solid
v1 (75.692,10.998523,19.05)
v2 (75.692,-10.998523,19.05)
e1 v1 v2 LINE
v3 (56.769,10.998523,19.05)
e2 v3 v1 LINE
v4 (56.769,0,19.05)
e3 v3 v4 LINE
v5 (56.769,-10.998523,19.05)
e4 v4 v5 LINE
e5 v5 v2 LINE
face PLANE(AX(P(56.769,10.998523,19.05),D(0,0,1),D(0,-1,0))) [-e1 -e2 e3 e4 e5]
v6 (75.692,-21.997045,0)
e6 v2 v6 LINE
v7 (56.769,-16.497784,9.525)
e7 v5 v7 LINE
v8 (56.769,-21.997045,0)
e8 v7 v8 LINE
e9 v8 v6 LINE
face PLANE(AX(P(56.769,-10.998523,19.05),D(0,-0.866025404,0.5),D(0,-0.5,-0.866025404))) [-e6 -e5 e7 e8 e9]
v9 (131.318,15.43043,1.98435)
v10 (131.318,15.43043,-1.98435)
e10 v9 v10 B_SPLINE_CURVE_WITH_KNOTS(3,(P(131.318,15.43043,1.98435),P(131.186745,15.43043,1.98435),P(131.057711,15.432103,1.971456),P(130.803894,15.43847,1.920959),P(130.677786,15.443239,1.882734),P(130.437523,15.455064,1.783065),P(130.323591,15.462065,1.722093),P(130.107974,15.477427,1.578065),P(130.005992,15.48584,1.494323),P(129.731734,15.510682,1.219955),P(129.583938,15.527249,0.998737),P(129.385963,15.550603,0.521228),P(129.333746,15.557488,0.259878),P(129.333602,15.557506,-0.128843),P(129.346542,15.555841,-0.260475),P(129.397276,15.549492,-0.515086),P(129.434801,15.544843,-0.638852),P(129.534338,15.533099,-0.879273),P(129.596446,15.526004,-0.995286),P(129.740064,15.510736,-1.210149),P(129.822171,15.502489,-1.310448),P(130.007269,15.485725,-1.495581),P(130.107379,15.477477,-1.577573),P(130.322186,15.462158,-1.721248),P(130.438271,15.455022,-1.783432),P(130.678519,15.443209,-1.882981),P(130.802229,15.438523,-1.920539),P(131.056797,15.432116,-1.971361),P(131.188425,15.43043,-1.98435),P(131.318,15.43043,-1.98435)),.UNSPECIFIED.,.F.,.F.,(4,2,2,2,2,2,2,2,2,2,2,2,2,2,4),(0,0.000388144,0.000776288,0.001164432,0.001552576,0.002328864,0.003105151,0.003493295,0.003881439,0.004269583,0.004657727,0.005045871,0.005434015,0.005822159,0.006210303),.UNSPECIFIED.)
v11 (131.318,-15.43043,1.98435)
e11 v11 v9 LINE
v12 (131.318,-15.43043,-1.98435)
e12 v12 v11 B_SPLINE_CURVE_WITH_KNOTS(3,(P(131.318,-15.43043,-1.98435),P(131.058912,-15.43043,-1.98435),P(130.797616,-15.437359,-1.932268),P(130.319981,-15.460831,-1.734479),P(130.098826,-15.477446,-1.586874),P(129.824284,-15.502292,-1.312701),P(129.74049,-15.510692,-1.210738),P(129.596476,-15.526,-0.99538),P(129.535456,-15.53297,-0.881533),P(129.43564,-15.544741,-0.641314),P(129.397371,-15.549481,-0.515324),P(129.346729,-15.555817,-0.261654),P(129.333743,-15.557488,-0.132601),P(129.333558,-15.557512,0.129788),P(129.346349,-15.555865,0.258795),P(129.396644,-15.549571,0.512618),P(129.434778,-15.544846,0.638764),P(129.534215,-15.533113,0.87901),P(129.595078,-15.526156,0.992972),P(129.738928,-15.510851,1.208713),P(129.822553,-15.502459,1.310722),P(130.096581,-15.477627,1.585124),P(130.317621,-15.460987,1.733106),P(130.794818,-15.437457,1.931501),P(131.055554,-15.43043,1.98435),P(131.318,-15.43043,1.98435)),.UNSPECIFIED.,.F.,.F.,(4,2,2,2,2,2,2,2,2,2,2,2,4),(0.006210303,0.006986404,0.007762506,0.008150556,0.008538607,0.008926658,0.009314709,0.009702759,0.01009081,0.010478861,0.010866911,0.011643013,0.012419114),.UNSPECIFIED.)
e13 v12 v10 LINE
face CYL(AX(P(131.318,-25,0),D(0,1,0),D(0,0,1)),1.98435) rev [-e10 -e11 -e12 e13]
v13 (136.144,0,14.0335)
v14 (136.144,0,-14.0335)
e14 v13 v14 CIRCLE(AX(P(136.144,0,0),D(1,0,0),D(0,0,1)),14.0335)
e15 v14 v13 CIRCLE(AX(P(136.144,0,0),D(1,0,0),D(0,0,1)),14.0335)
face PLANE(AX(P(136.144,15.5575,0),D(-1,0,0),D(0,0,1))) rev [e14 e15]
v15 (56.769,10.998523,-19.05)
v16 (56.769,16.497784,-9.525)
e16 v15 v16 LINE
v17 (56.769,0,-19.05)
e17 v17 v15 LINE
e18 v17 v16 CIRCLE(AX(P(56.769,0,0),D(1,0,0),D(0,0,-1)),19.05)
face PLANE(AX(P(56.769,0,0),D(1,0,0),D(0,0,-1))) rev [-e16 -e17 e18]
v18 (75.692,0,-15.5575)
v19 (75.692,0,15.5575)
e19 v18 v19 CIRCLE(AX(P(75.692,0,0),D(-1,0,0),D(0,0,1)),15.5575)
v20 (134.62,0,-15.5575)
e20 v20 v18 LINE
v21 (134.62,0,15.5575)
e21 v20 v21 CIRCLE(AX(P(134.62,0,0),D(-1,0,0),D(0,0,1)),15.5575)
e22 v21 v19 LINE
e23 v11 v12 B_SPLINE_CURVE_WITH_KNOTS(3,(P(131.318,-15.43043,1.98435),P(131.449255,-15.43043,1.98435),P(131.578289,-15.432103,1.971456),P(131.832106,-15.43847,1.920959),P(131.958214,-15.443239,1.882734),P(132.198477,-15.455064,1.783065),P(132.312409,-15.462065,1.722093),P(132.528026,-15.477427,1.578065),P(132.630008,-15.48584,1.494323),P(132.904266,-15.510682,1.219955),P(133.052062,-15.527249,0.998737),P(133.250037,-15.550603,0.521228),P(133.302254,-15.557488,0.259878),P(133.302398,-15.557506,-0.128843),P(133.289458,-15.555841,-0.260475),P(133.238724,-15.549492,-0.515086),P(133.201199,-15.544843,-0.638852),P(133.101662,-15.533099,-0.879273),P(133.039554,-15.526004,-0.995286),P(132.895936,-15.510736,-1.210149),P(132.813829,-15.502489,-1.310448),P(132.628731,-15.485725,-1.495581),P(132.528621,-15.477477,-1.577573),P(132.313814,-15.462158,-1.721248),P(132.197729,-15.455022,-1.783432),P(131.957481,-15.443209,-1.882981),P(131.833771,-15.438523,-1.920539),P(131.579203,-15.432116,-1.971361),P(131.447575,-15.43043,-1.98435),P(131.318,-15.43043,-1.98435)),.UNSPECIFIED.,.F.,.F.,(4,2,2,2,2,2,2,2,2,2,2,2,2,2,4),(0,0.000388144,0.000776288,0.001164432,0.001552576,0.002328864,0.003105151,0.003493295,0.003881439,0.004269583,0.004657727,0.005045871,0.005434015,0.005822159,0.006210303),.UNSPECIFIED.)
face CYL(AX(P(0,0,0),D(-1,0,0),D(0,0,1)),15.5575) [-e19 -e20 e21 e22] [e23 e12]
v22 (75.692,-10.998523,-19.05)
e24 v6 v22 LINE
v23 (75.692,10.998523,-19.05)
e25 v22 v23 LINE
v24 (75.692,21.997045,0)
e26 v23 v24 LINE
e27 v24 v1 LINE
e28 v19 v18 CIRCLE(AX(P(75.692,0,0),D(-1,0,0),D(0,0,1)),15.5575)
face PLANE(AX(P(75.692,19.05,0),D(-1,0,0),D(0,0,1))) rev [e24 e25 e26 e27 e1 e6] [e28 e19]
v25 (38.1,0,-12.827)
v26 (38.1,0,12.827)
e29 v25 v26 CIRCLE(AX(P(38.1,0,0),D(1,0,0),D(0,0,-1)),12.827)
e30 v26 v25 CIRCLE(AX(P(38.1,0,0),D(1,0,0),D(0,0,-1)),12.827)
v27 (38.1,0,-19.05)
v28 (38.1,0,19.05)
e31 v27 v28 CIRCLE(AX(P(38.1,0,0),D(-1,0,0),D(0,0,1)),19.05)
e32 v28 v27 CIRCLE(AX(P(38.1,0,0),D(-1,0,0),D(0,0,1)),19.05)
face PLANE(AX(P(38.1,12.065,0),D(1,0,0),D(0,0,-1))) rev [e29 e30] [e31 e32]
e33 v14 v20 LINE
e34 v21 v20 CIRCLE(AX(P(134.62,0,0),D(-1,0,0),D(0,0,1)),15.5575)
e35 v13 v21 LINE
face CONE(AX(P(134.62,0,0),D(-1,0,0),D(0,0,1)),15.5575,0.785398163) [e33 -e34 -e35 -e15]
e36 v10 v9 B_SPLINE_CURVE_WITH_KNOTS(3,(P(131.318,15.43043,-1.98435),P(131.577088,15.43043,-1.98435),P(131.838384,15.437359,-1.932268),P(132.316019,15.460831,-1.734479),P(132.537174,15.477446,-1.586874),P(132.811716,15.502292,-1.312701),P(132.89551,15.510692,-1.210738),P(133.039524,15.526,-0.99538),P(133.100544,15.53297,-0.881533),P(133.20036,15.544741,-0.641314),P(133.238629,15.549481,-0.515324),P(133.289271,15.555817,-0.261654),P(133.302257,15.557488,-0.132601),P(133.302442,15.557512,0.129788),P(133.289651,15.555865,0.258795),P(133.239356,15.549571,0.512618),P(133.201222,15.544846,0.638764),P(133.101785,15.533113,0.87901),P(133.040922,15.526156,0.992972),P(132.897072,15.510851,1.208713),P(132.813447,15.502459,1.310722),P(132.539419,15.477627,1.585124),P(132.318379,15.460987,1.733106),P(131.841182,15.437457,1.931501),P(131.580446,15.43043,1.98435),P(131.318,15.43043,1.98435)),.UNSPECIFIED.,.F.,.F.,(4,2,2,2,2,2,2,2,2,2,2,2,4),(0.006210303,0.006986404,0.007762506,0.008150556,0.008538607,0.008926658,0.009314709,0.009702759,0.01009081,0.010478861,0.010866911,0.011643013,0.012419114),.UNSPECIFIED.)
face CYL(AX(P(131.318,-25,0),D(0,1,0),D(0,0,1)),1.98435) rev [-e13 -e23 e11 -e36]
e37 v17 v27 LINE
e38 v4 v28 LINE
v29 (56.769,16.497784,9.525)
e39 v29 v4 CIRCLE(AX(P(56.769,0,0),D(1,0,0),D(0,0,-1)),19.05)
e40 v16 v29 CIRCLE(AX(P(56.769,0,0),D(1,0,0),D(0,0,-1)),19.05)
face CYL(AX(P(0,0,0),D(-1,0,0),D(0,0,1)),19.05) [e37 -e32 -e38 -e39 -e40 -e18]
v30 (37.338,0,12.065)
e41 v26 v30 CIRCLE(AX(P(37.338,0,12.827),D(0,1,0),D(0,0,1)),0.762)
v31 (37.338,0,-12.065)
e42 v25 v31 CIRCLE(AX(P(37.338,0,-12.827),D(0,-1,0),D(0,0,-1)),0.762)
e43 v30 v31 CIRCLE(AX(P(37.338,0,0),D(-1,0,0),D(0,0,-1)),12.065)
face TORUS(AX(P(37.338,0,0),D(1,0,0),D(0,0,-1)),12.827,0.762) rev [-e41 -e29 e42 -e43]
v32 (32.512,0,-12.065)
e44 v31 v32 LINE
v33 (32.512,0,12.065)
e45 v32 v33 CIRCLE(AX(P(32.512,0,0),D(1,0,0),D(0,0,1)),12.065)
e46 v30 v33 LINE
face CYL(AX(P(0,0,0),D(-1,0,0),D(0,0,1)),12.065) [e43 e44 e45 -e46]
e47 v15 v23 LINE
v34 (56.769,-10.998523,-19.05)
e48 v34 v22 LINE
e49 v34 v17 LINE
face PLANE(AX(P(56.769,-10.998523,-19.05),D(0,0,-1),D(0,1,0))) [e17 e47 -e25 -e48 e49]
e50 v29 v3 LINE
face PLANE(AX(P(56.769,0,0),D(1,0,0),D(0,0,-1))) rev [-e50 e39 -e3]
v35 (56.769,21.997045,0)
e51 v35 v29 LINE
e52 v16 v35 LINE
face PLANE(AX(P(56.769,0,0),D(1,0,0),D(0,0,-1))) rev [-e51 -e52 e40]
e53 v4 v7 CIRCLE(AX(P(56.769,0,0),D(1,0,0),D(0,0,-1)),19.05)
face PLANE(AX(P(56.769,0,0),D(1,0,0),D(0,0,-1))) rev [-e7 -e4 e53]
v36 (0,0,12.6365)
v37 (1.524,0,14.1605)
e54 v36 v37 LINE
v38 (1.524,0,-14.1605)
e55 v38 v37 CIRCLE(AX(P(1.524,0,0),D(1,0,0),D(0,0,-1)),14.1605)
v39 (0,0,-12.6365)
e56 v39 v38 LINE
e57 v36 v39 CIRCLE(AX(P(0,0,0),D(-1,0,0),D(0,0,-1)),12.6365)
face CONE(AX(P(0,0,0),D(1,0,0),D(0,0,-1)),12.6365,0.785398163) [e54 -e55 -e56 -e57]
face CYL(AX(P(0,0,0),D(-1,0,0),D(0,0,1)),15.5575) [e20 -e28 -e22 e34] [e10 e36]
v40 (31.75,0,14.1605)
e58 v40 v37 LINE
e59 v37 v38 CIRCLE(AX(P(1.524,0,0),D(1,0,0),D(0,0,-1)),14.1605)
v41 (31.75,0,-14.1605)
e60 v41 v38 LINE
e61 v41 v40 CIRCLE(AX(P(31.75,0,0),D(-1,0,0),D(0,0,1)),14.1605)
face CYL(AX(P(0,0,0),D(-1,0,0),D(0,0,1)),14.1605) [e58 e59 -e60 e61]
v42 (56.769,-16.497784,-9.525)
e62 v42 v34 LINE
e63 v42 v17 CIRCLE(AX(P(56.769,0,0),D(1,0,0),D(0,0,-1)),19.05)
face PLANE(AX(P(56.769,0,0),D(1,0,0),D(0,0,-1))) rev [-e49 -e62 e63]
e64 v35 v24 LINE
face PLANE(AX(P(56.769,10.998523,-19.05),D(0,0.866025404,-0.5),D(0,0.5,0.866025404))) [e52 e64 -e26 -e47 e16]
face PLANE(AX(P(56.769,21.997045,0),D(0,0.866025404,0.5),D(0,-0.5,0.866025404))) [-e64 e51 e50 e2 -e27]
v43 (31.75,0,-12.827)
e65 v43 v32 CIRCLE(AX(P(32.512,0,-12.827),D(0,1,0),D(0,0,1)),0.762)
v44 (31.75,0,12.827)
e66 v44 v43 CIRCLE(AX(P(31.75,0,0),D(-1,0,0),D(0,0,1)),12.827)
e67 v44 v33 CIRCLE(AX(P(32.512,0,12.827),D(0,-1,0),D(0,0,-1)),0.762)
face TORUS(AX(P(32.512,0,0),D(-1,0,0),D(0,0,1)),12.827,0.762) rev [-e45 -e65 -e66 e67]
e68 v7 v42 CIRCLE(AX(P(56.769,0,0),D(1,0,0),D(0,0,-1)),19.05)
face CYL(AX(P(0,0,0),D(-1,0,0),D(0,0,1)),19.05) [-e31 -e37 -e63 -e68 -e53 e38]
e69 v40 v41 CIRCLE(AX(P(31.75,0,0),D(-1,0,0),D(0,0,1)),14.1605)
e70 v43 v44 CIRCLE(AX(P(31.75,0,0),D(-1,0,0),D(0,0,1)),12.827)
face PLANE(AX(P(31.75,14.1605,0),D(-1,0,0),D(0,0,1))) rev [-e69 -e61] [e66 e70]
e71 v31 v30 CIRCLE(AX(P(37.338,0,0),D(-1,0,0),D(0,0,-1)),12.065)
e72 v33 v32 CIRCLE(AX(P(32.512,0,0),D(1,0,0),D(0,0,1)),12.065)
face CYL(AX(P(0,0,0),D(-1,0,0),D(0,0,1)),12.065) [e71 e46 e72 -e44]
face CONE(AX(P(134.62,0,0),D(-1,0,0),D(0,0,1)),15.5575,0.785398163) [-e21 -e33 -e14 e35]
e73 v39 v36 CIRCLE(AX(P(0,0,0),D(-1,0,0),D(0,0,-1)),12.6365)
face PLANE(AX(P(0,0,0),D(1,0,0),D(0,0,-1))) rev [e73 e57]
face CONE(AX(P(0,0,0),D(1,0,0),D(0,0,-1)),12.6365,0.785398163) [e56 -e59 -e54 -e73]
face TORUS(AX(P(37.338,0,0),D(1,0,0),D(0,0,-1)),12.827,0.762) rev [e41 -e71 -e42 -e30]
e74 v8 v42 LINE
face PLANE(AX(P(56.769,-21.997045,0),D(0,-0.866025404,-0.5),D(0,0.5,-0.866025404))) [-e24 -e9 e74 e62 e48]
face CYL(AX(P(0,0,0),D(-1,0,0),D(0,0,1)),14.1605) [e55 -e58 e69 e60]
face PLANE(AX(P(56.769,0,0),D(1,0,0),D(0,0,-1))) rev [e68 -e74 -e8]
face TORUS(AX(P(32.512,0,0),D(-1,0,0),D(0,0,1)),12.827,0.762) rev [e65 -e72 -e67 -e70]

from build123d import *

# Parameters (mm, degrees)
CHAMFER1_SIZE       = 1.524
BOSS_EXTRUDE1_DEPTH = 18.923
FILLET1_R           = 0.762
SKETCH3_R           = 1.98435
CUT_EXTRUDE1_DEPTH  = 25


with BuildPart() as part:
    # Sketch1 → Revolve1 (revolve)
    with BuildSketch(Plane.XY, mode=Mode.PRIVATE) as revolve1_sk:
        Polygon((0, 0), (0, 14.1605), (31.75, 14.1605), (31.75, 12.065), (38.1, 12.065), (38.1, 19.05), (75.692, 19.05), (75.692, 15.5575), (136.144, 15.5575), (136.144, 0), align=None)
    revolve(revolve1_sk.sketch.rotate(Axis((0, 0, 0), (1, 0, 0)), 90), axis=Axis((0, 0, 0), (1, 0, 0)))

    # Chamfer1
    chamfer1_edges = [part.edges().sort_by_distance(p)[0] for p in [
        (0, 0, -14.1605),
        (136.144, 0, -15.5575),
    ]]
    chamfer(chamfer1_edges, length=CHAMFER1_SIZE)

    # Sketch2 → Boss-Extrude1 (add)
    with BuildSketch(Plane(origin=(75.692, 0, 0), x_dir=(0, 0, -1), z_dir=(1, 0, 0))):
        Polygon((0, 21.997045256), (-19.05, 10.998522628), (-19.05, -10.998522628), (0, -21.997045256), (19.05, -10.998522628), (19.05, 10.998522628), align=None)
    extrude(amount=-BOSS_EXTRUDE1_DEPTH)

    # Fillet1
    fillet1_edges = [part.edges().sort_by_distance(p)[0] for p in [
        (38.1, 0, -12.065),
        (31.75, 0, -12.065),
    ]]
    fillet(fillet1_edges, radius=FILLET1_R)

    # Sketch3 → Cut-Extrude1 (cut, symmetric)
    with BuildSketch(Plane(origin=(0, 0, 0), x_dir=(1, 0, 0), z_dir=(0, 1, 0))):
        with Locations(Location((131.318, 0, 0), (0, 0, 270))):
            Circle(SKETCH3_R)
    extrude(amount=CUT_EXTRUDE1_DEPTH, both=True, mode=Mode.SUBTRACT)


solid = part.part
